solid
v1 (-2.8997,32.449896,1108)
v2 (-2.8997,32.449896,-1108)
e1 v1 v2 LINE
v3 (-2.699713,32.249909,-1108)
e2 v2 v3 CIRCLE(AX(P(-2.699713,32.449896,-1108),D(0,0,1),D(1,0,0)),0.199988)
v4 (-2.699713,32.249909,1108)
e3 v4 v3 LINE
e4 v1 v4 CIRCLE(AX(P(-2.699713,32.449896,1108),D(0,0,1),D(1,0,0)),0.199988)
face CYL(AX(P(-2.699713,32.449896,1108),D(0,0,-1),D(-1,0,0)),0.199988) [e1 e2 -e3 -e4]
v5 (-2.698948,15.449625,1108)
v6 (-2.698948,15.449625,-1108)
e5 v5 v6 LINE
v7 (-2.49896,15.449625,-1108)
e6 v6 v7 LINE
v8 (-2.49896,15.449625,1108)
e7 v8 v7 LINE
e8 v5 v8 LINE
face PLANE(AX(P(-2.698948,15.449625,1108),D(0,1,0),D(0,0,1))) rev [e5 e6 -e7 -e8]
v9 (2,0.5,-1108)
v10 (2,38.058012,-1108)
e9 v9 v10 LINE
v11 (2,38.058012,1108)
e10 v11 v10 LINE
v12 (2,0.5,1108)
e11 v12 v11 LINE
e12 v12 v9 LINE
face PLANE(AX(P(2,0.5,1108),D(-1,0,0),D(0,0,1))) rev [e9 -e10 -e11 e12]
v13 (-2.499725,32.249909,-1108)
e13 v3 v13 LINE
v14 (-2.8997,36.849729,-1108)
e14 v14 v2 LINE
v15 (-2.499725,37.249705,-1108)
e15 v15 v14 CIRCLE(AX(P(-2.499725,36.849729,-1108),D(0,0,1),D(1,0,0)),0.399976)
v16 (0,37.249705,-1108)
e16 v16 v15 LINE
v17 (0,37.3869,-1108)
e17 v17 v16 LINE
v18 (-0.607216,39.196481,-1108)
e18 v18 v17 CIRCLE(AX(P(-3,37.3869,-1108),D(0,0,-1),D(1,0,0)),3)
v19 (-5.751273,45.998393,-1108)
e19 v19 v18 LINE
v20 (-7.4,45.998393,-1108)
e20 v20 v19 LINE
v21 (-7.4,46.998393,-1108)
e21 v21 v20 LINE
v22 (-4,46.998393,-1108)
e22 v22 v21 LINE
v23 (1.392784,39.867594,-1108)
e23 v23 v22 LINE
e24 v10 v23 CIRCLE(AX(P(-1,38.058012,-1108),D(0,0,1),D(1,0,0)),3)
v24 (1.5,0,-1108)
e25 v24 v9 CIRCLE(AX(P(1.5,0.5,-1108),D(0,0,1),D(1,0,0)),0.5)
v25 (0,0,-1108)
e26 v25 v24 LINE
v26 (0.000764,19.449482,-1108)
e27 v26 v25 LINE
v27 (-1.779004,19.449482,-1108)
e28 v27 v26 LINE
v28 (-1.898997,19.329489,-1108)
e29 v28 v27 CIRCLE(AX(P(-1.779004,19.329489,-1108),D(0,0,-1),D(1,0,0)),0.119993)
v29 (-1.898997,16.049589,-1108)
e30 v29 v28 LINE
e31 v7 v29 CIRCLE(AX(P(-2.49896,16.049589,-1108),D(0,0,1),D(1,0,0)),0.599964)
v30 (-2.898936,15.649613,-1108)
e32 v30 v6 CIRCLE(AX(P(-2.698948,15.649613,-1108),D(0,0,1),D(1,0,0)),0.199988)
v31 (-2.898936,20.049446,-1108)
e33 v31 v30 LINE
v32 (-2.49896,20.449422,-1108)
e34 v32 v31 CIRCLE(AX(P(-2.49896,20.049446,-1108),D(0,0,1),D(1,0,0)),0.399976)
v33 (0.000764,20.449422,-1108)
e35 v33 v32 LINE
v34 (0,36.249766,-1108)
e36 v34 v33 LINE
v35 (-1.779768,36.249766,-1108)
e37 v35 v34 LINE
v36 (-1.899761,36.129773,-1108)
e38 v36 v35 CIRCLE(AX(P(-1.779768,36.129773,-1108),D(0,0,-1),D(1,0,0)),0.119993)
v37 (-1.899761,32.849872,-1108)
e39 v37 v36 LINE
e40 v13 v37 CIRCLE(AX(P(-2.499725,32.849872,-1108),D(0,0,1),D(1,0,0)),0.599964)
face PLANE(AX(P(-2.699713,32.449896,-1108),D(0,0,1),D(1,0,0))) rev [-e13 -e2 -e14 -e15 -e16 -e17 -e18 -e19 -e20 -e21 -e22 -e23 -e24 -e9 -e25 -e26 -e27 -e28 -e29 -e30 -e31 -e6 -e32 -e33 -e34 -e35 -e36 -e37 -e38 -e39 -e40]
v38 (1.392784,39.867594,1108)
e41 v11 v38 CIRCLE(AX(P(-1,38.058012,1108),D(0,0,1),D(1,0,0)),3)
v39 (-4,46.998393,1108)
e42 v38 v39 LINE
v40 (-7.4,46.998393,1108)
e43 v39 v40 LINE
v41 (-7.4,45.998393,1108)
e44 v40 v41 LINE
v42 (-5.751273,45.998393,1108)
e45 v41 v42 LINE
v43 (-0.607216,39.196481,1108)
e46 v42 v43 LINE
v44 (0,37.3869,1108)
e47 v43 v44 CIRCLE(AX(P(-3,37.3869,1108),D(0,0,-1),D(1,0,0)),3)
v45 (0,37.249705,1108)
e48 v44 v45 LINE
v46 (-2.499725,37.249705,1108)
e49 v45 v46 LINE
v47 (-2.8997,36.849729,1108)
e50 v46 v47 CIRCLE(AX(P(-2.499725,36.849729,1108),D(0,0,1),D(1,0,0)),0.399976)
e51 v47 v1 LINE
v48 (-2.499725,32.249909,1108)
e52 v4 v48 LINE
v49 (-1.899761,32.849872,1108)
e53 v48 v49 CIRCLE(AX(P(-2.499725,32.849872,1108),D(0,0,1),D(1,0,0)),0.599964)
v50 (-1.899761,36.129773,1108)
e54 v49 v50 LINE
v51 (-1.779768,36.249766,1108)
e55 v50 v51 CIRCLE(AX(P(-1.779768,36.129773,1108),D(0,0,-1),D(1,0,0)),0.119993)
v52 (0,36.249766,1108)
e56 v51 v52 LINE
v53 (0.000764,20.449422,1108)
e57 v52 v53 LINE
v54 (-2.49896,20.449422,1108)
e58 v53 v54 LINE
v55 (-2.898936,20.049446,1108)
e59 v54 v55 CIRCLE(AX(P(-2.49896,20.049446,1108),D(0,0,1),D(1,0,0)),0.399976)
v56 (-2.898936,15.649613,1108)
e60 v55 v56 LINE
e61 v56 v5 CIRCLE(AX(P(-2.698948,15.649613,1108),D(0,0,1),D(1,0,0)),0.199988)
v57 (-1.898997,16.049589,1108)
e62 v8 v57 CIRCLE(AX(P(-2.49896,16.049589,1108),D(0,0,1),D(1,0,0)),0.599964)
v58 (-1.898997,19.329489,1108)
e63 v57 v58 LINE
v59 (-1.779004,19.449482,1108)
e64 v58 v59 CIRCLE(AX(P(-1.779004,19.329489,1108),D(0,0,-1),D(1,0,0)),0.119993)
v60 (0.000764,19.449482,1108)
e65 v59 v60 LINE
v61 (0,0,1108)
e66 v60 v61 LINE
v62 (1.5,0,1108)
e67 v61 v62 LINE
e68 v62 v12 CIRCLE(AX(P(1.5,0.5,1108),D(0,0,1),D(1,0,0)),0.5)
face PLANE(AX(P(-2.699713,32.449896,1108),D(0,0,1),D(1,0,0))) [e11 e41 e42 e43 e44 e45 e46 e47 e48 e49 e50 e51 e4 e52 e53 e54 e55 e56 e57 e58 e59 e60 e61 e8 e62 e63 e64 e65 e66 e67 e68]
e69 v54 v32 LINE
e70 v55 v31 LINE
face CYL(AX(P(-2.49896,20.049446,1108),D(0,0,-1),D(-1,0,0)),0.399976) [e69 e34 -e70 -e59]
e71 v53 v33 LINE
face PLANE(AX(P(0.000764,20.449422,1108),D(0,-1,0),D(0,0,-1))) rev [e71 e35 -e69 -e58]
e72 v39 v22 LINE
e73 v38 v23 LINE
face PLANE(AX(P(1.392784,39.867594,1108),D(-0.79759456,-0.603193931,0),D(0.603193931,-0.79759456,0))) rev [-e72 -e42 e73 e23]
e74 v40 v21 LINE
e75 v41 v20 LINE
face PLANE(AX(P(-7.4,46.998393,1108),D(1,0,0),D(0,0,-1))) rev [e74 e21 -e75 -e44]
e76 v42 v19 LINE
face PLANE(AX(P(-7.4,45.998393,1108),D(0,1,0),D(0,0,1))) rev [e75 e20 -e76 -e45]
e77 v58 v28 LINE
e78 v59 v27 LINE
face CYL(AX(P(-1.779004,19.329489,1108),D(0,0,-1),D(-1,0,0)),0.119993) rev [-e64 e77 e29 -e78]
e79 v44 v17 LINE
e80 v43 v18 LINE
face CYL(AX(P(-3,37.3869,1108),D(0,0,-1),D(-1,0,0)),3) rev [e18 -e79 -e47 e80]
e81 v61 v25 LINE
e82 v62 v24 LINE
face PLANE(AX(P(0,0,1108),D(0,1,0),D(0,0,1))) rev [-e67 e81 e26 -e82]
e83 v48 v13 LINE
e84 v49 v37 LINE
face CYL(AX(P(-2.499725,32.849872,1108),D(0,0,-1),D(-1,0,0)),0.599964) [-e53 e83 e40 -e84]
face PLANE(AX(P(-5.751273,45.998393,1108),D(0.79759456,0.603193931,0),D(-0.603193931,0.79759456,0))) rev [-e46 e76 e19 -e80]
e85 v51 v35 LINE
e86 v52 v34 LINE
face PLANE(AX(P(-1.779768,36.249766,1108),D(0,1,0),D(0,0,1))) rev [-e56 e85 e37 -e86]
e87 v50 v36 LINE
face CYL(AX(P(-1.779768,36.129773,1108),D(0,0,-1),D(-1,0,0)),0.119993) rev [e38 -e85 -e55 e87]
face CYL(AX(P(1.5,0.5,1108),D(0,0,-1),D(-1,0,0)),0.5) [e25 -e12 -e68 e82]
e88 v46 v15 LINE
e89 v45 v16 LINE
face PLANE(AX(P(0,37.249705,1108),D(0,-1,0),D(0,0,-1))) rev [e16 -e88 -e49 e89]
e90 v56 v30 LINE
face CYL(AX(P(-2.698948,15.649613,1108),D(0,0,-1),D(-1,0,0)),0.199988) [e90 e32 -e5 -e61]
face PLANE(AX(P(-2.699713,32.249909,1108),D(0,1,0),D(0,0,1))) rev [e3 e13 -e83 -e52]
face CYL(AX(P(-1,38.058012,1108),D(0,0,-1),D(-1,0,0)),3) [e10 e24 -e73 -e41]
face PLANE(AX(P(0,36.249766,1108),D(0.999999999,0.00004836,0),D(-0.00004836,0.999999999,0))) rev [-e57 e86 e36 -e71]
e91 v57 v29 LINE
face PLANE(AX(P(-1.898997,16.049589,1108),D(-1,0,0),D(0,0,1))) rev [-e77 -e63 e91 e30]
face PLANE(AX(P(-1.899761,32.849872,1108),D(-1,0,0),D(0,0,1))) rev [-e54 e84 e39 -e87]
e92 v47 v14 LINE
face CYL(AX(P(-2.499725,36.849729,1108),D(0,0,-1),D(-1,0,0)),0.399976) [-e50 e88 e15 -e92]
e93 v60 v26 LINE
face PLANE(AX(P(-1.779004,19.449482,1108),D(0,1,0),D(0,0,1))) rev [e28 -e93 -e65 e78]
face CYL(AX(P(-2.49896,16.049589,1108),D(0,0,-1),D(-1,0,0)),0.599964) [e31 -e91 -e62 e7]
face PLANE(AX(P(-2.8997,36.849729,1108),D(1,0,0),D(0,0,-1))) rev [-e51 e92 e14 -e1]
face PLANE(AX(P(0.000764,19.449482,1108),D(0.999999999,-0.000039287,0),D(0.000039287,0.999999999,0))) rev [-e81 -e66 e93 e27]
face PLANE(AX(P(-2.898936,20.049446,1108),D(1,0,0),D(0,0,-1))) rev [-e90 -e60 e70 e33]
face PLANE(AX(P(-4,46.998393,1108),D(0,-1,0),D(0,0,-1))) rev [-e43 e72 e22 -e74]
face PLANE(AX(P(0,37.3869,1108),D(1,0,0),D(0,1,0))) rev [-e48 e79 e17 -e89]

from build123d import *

# Parameters (mm, degrees)
EXTRUDE_1_DEPTH = 1108


with BuildPart() as part:
    # 草图2 → 凸台-拉伸1 (new, symmetric)
    with BuildSketch(Plane.XY):
        with BuildLine():
            Line((-2.699712502, 32.249908534), (-2.499724552, 32.249908534))
            ThreePointArc((-2.499724552, 32.249908534), (-2.075486045, 32.425633877), (-1.899760702, 32.849872384))
            Line((-1.899760702, 32.849872384), (-1.899760702, 36.12977276))
            ThreePointArc((-1.899760702, 36.12977276), (-1.864615633, 36.214620461), (-1.779767932, 36.24976553))
            Line((-1.779767932, 36.24976553), (0, 36.24976553))
            Line((0, 36.24976553), (0.000764104, 20.44942184))
            Line((0.000764104, 20.44942184), (-2.498960448, 20.44942184))
            ThreePointArc((-2.498960448, 20.44942184), (-2.781786119, 20.332271611), (-2.898936348, 20.04944594))
            Line((-2.898936348, 20.04944594), (-2.898936348, 15.649613044))
            ThreePointArc((-2.898936348, 15.649613044), (-2.840361233, 15.508200208), (-2.698948398, 15.449625094))
            Line((-2.698948398, 15.449625094), (-2.498960448, 15.449625094))
            ThreePointArc((-2.498960448, 15.449625094), (-2.074721941, 15.625350437), (-1.898996598, 16.049588944))
            Line((-1.898996598, 16.049588944), (-1.898996598, 19.32948932))
            ThreePointArc((-1.898996598, 19.32948932), (-1.863851529, 19.414337021), (-1.779003828, 19.44948209))
            Line((-1.779003828, 19.44948209), (0.000764104, 19.44948209))
            Line((0.000764104, 19.44948209), (0, 0))
            Line((0, 0), (1.5, 0))
            ThreePointArc((1.5, 0), (1.853553391, 0.146446609), (2, 0.5))
            Line((2, 0.5), (2, 38.058011928))
            ThreePointArc((2, 38.058011928), (1.844147591, 39.012383177), (1.392783679, 39.867593721))
            Line((1.392783679, 39.867593721), (-4, 46.998393128))
            Line((-4, 46.998393128), (-7.4, 46.998393128))
            Line((-7.4, 46.998393128), (-7.4, 45.998393128))
            Line((-7.4, 45.998393128), (-5.751273316, 45.998393128))
            Line((-5.751273316, 45.998393128), (-0.607216321, 39.196481397))
            ThreePointArc((-0.607216321, 39.196481397), (-0.155852409, 38.341270854), (0, 37.386899605))
            Line((0, 37.386899605), (0, 37.24970528))
            Line((0, 37.24970528), (-2.499724552, 37.24970528))
            ThreePointArc((-2.499724552, 37.24970528), (-2.782550223, 37.132555051), (-2.899700452, 36.84972938))
            Line((-2.899700452, 36.84972938), (-2.899700452, 32.449896484))
            ThreePointArc((-2.899700452, 32.449896484), (-2.841125337, 32.308483648), (-2.699712502, 32.249908534))
        make_face()
    extrude(amount=EXTRUDE_1_DEPTH, both=True)


solid = part.part
